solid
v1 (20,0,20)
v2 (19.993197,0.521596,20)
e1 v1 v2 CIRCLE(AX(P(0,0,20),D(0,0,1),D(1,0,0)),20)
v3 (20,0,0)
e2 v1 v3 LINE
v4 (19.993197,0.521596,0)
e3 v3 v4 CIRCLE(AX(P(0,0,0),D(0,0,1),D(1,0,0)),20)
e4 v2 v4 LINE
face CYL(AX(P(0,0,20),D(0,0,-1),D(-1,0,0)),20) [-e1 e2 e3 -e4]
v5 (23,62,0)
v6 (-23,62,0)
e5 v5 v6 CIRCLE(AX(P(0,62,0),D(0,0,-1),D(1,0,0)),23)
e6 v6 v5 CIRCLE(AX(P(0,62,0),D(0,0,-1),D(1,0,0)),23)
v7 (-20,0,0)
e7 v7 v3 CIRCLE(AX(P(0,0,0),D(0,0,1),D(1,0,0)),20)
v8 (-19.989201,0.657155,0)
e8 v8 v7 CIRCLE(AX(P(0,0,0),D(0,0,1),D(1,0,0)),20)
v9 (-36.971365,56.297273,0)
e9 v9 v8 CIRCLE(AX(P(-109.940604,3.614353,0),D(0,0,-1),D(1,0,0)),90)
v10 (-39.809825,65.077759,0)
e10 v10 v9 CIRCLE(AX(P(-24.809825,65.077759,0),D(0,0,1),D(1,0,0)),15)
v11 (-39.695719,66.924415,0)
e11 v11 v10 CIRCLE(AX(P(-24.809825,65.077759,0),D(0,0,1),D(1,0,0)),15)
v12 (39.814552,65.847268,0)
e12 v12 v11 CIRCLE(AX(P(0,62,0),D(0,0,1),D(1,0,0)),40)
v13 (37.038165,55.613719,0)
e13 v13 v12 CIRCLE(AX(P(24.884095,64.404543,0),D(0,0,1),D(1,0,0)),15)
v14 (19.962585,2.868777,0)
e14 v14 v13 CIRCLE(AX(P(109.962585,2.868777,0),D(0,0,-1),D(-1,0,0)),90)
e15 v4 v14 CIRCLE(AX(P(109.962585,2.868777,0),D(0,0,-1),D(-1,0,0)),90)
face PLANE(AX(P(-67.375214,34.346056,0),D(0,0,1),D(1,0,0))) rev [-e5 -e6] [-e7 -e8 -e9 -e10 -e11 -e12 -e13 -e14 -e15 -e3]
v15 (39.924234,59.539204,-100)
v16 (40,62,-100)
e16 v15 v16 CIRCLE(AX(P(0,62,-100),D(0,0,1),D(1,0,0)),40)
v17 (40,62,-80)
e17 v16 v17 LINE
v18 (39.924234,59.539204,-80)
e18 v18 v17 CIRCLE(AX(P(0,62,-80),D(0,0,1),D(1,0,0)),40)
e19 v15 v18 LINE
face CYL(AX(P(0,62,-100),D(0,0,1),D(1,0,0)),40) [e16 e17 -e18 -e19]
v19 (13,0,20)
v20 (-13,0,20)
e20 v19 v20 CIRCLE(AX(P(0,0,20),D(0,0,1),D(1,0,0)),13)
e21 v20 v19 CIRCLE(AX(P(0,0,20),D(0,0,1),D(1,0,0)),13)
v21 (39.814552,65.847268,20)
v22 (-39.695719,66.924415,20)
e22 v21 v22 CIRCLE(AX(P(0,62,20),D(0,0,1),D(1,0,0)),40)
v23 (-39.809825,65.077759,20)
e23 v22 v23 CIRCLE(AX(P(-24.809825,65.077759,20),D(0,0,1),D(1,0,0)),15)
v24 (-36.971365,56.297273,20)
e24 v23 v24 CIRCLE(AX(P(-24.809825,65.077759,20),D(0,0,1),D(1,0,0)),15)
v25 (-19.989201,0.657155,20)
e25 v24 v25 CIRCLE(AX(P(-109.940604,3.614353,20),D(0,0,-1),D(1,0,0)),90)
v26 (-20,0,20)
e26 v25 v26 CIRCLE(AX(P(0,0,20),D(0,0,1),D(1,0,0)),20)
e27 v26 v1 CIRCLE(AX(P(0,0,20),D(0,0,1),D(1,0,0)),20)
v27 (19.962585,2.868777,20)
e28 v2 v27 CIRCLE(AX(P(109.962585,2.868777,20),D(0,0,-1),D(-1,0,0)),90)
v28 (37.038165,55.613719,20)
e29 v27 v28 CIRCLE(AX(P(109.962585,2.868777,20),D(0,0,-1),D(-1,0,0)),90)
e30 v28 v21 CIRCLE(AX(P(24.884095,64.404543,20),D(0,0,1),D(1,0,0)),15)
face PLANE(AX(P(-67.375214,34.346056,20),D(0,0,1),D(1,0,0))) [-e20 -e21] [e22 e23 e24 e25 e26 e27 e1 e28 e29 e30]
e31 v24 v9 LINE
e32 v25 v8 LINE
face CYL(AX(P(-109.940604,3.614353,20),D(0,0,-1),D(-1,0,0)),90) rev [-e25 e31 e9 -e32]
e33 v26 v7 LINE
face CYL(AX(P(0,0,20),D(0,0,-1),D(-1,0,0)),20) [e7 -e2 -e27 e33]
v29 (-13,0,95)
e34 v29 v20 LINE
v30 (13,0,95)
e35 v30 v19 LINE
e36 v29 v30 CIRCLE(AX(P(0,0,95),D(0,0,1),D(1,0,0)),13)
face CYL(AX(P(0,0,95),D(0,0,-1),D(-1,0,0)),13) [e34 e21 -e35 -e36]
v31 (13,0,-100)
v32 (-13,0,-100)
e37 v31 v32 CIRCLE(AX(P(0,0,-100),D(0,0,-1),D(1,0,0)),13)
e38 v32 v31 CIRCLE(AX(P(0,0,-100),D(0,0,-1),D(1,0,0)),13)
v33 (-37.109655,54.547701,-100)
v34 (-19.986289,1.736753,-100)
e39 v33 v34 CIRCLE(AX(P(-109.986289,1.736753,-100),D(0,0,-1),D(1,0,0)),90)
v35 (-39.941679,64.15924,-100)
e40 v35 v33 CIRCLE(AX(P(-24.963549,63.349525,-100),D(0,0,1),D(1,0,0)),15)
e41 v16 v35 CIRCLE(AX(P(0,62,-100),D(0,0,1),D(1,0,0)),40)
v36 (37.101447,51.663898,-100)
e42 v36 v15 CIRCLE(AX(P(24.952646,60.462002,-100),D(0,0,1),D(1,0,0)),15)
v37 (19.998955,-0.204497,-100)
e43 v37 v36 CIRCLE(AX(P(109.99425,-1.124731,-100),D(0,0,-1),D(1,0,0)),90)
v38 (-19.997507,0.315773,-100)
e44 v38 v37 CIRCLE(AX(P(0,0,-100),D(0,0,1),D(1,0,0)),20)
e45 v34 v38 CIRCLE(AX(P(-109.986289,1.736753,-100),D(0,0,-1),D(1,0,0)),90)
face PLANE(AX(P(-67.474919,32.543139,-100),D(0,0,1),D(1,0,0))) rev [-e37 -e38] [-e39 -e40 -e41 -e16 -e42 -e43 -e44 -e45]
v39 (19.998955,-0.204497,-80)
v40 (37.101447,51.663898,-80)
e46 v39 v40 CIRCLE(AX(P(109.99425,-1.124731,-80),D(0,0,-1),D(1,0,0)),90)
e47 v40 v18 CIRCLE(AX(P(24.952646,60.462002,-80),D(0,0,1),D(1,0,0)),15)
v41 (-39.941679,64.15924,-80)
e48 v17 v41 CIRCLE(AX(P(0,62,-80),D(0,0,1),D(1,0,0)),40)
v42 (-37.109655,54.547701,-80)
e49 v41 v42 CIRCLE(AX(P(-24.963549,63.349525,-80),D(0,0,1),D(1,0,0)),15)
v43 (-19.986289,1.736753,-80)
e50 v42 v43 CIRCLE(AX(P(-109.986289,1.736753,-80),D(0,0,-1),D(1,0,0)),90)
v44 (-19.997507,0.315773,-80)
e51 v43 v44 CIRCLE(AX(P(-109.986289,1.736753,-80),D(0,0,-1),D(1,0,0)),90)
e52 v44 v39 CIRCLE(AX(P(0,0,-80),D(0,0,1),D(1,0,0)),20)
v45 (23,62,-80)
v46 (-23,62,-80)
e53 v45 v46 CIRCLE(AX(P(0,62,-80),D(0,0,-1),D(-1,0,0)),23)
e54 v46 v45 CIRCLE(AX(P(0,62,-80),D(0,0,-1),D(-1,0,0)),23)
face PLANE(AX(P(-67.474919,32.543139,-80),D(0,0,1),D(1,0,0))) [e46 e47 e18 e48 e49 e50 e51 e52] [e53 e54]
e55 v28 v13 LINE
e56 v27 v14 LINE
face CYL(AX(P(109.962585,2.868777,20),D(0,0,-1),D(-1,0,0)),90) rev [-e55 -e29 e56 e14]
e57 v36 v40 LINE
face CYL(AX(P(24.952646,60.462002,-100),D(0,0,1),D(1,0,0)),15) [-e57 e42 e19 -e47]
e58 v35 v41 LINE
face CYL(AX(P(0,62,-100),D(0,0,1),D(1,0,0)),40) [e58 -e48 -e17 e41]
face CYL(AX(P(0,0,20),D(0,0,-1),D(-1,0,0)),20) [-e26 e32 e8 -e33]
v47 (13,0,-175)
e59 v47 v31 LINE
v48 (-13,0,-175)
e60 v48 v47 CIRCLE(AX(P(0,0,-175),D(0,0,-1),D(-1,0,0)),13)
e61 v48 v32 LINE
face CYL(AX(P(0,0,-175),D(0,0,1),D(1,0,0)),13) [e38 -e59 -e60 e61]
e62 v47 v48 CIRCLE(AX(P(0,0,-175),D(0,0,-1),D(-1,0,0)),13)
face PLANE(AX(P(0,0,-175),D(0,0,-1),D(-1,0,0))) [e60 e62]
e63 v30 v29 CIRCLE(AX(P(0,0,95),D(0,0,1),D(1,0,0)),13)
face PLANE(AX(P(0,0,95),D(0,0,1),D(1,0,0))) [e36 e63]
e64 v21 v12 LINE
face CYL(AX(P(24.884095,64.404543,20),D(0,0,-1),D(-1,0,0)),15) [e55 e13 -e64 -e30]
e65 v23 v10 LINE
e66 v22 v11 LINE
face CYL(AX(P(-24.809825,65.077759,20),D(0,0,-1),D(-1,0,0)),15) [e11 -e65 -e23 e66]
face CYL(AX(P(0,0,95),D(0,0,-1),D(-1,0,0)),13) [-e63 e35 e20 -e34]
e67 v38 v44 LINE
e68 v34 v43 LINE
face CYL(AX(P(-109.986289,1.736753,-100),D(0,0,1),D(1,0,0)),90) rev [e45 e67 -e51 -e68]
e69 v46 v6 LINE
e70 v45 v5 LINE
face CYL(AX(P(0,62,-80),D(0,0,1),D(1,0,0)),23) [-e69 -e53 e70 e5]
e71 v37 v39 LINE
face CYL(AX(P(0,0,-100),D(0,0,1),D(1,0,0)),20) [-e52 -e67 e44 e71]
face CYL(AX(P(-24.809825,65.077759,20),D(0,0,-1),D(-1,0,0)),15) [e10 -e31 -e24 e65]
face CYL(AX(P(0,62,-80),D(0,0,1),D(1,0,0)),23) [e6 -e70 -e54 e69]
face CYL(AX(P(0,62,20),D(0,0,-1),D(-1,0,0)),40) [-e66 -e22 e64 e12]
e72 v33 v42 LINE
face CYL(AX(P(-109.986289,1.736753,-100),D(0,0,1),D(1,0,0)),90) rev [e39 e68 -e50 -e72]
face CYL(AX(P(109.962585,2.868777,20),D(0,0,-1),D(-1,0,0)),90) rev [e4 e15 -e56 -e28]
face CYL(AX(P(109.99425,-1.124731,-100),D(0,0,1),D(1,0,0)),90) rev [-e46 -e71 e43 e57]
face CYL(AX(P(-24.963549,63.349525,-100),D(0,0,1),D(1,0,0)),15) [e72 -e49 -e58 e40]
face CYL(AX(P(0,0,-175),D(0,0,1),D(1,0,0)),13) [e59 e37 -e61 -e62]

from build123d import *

# Parameters (mm, degrees)
FRONT_PLATE_DEPTH      = 20
FRONT_PIN_PROFILE_26_R = 13
FRONT_PIN_26_DEPTH     = 75
JOURNAL_PROFILE_46_R   = 23
JOURNAL_46_DEPTH       = 80
REAR_START             = -20
REAR_PLATE_DEPTH       = 20
REAR_START_2           = 75
REAR_PIN_PROFILE_26_R  = 13
REAR_PIN_26_DEPTH      = 75


with BuildPart() as part:
    # Front Plate Profile → Front Plate (new body)
    with BuildSketch(Plane.XY):
        with BuildLine():
            ThreePointArc((-19.989200766, 0.657155043), (-0.067809086, -19.999885048), (19.993197289, 0.52159577))
            ThreePointArc((19.993197289, 0.52159577), (23.983612751, 29.469835271), (37.03816485, 55.613718978))
            ThreePointArc((37.03816485, 55.613718978), (39.360775458, 60.47698398), (39.814551695, 65.847268297))
            ThreePointArc((39.814551695, 65.847268297), (0.541840926, 101.996329937), (-39.695719365, 66.9244151))
            ThreePointArc((-39.695719365, 66.9244151), (-39.339964644, 61.352839249), (-36.971364547, 56.297272766))
            ThreePointArc((-36.971364547, 56.297272766), (-23.860759515, 29.887158775), (-19.989200766, 0.657155043))
        make_face()
    extrude(amount=FRONT_PLATE_DEPTH)

    # Front Pin Profile Ø26 → Front Pin Ø26 (add)
    with BuildSketch(Plane.XY.offset(20)):
        Circle(FRONT_PIN_PROFILE_26_R)
    extrude(amount=FRONT_PIN_26_DEPTH)

    # Journal Profile Ø46 → Journal Ø46 (add)
    with BuildSketch(Plane(origin=(0, 0, 0), x_dir=(-1, 0, 0), z_dir=(0, 0, -1))):
        with Locations(Location((0, 62, 0), (0, 0, 180))):
            Circle(JOURNAL_PROFILE_46_R)
    extrude(amount=JOURNAL_46_DEPTH)

    # Rear Plate Profile → Rear Plate (add)
    with BuildSketch(Plane.XY.offset(-80).offset(REAR_START)):
        with BuildLine():
            ThreePointArc((-19.997507027, 0.315773186), (-0.260135851, -19.998308162), (19.998954502, -0.204496502))
            ThreePointArc((19.998954502, -0.204496502), (24.520770215, 27.058319007), (37.101446898, 51.663897663))
            ThreePointArc((37.101446898, 51.663897663), (39.072985568, 55.400775042), (39.924234273, 59.539203839))
            ThreePointArc((39.924234273, 59.539203839), (2.310034684, 101.933241038), (-39.941678501, 64.159240274))
            ThreePointArc((-39.941678501, 64.159240274), (-39.351963031, 59.110003561), (-37.109654718, 54.547700507))
            ThreePointArc((-37.109654718, 54.547700507), (-24.157614064, 28.818824435), (-19.997507027, 0.315773186))
        make_face()
    extrude(amount=REAR_PLATE_DEPTH)

    # Rear Pin Profile Ø26 → Rear Pin Ø26 (add)
    with BuildSketch(Plane(origin=(0, 0, -100), x_dir=(-1, 0, 0), z_dir=(0, 0, -1)).offset(REAR_START_2)):
        with Locations(Location((0, 0, 0), (0, 0, 180))):
            Circle(REAR_PIN_PROFILE_26_R)
    extrude(amount=-REAR_PIN_26_DEPTH)


solid = part.part
